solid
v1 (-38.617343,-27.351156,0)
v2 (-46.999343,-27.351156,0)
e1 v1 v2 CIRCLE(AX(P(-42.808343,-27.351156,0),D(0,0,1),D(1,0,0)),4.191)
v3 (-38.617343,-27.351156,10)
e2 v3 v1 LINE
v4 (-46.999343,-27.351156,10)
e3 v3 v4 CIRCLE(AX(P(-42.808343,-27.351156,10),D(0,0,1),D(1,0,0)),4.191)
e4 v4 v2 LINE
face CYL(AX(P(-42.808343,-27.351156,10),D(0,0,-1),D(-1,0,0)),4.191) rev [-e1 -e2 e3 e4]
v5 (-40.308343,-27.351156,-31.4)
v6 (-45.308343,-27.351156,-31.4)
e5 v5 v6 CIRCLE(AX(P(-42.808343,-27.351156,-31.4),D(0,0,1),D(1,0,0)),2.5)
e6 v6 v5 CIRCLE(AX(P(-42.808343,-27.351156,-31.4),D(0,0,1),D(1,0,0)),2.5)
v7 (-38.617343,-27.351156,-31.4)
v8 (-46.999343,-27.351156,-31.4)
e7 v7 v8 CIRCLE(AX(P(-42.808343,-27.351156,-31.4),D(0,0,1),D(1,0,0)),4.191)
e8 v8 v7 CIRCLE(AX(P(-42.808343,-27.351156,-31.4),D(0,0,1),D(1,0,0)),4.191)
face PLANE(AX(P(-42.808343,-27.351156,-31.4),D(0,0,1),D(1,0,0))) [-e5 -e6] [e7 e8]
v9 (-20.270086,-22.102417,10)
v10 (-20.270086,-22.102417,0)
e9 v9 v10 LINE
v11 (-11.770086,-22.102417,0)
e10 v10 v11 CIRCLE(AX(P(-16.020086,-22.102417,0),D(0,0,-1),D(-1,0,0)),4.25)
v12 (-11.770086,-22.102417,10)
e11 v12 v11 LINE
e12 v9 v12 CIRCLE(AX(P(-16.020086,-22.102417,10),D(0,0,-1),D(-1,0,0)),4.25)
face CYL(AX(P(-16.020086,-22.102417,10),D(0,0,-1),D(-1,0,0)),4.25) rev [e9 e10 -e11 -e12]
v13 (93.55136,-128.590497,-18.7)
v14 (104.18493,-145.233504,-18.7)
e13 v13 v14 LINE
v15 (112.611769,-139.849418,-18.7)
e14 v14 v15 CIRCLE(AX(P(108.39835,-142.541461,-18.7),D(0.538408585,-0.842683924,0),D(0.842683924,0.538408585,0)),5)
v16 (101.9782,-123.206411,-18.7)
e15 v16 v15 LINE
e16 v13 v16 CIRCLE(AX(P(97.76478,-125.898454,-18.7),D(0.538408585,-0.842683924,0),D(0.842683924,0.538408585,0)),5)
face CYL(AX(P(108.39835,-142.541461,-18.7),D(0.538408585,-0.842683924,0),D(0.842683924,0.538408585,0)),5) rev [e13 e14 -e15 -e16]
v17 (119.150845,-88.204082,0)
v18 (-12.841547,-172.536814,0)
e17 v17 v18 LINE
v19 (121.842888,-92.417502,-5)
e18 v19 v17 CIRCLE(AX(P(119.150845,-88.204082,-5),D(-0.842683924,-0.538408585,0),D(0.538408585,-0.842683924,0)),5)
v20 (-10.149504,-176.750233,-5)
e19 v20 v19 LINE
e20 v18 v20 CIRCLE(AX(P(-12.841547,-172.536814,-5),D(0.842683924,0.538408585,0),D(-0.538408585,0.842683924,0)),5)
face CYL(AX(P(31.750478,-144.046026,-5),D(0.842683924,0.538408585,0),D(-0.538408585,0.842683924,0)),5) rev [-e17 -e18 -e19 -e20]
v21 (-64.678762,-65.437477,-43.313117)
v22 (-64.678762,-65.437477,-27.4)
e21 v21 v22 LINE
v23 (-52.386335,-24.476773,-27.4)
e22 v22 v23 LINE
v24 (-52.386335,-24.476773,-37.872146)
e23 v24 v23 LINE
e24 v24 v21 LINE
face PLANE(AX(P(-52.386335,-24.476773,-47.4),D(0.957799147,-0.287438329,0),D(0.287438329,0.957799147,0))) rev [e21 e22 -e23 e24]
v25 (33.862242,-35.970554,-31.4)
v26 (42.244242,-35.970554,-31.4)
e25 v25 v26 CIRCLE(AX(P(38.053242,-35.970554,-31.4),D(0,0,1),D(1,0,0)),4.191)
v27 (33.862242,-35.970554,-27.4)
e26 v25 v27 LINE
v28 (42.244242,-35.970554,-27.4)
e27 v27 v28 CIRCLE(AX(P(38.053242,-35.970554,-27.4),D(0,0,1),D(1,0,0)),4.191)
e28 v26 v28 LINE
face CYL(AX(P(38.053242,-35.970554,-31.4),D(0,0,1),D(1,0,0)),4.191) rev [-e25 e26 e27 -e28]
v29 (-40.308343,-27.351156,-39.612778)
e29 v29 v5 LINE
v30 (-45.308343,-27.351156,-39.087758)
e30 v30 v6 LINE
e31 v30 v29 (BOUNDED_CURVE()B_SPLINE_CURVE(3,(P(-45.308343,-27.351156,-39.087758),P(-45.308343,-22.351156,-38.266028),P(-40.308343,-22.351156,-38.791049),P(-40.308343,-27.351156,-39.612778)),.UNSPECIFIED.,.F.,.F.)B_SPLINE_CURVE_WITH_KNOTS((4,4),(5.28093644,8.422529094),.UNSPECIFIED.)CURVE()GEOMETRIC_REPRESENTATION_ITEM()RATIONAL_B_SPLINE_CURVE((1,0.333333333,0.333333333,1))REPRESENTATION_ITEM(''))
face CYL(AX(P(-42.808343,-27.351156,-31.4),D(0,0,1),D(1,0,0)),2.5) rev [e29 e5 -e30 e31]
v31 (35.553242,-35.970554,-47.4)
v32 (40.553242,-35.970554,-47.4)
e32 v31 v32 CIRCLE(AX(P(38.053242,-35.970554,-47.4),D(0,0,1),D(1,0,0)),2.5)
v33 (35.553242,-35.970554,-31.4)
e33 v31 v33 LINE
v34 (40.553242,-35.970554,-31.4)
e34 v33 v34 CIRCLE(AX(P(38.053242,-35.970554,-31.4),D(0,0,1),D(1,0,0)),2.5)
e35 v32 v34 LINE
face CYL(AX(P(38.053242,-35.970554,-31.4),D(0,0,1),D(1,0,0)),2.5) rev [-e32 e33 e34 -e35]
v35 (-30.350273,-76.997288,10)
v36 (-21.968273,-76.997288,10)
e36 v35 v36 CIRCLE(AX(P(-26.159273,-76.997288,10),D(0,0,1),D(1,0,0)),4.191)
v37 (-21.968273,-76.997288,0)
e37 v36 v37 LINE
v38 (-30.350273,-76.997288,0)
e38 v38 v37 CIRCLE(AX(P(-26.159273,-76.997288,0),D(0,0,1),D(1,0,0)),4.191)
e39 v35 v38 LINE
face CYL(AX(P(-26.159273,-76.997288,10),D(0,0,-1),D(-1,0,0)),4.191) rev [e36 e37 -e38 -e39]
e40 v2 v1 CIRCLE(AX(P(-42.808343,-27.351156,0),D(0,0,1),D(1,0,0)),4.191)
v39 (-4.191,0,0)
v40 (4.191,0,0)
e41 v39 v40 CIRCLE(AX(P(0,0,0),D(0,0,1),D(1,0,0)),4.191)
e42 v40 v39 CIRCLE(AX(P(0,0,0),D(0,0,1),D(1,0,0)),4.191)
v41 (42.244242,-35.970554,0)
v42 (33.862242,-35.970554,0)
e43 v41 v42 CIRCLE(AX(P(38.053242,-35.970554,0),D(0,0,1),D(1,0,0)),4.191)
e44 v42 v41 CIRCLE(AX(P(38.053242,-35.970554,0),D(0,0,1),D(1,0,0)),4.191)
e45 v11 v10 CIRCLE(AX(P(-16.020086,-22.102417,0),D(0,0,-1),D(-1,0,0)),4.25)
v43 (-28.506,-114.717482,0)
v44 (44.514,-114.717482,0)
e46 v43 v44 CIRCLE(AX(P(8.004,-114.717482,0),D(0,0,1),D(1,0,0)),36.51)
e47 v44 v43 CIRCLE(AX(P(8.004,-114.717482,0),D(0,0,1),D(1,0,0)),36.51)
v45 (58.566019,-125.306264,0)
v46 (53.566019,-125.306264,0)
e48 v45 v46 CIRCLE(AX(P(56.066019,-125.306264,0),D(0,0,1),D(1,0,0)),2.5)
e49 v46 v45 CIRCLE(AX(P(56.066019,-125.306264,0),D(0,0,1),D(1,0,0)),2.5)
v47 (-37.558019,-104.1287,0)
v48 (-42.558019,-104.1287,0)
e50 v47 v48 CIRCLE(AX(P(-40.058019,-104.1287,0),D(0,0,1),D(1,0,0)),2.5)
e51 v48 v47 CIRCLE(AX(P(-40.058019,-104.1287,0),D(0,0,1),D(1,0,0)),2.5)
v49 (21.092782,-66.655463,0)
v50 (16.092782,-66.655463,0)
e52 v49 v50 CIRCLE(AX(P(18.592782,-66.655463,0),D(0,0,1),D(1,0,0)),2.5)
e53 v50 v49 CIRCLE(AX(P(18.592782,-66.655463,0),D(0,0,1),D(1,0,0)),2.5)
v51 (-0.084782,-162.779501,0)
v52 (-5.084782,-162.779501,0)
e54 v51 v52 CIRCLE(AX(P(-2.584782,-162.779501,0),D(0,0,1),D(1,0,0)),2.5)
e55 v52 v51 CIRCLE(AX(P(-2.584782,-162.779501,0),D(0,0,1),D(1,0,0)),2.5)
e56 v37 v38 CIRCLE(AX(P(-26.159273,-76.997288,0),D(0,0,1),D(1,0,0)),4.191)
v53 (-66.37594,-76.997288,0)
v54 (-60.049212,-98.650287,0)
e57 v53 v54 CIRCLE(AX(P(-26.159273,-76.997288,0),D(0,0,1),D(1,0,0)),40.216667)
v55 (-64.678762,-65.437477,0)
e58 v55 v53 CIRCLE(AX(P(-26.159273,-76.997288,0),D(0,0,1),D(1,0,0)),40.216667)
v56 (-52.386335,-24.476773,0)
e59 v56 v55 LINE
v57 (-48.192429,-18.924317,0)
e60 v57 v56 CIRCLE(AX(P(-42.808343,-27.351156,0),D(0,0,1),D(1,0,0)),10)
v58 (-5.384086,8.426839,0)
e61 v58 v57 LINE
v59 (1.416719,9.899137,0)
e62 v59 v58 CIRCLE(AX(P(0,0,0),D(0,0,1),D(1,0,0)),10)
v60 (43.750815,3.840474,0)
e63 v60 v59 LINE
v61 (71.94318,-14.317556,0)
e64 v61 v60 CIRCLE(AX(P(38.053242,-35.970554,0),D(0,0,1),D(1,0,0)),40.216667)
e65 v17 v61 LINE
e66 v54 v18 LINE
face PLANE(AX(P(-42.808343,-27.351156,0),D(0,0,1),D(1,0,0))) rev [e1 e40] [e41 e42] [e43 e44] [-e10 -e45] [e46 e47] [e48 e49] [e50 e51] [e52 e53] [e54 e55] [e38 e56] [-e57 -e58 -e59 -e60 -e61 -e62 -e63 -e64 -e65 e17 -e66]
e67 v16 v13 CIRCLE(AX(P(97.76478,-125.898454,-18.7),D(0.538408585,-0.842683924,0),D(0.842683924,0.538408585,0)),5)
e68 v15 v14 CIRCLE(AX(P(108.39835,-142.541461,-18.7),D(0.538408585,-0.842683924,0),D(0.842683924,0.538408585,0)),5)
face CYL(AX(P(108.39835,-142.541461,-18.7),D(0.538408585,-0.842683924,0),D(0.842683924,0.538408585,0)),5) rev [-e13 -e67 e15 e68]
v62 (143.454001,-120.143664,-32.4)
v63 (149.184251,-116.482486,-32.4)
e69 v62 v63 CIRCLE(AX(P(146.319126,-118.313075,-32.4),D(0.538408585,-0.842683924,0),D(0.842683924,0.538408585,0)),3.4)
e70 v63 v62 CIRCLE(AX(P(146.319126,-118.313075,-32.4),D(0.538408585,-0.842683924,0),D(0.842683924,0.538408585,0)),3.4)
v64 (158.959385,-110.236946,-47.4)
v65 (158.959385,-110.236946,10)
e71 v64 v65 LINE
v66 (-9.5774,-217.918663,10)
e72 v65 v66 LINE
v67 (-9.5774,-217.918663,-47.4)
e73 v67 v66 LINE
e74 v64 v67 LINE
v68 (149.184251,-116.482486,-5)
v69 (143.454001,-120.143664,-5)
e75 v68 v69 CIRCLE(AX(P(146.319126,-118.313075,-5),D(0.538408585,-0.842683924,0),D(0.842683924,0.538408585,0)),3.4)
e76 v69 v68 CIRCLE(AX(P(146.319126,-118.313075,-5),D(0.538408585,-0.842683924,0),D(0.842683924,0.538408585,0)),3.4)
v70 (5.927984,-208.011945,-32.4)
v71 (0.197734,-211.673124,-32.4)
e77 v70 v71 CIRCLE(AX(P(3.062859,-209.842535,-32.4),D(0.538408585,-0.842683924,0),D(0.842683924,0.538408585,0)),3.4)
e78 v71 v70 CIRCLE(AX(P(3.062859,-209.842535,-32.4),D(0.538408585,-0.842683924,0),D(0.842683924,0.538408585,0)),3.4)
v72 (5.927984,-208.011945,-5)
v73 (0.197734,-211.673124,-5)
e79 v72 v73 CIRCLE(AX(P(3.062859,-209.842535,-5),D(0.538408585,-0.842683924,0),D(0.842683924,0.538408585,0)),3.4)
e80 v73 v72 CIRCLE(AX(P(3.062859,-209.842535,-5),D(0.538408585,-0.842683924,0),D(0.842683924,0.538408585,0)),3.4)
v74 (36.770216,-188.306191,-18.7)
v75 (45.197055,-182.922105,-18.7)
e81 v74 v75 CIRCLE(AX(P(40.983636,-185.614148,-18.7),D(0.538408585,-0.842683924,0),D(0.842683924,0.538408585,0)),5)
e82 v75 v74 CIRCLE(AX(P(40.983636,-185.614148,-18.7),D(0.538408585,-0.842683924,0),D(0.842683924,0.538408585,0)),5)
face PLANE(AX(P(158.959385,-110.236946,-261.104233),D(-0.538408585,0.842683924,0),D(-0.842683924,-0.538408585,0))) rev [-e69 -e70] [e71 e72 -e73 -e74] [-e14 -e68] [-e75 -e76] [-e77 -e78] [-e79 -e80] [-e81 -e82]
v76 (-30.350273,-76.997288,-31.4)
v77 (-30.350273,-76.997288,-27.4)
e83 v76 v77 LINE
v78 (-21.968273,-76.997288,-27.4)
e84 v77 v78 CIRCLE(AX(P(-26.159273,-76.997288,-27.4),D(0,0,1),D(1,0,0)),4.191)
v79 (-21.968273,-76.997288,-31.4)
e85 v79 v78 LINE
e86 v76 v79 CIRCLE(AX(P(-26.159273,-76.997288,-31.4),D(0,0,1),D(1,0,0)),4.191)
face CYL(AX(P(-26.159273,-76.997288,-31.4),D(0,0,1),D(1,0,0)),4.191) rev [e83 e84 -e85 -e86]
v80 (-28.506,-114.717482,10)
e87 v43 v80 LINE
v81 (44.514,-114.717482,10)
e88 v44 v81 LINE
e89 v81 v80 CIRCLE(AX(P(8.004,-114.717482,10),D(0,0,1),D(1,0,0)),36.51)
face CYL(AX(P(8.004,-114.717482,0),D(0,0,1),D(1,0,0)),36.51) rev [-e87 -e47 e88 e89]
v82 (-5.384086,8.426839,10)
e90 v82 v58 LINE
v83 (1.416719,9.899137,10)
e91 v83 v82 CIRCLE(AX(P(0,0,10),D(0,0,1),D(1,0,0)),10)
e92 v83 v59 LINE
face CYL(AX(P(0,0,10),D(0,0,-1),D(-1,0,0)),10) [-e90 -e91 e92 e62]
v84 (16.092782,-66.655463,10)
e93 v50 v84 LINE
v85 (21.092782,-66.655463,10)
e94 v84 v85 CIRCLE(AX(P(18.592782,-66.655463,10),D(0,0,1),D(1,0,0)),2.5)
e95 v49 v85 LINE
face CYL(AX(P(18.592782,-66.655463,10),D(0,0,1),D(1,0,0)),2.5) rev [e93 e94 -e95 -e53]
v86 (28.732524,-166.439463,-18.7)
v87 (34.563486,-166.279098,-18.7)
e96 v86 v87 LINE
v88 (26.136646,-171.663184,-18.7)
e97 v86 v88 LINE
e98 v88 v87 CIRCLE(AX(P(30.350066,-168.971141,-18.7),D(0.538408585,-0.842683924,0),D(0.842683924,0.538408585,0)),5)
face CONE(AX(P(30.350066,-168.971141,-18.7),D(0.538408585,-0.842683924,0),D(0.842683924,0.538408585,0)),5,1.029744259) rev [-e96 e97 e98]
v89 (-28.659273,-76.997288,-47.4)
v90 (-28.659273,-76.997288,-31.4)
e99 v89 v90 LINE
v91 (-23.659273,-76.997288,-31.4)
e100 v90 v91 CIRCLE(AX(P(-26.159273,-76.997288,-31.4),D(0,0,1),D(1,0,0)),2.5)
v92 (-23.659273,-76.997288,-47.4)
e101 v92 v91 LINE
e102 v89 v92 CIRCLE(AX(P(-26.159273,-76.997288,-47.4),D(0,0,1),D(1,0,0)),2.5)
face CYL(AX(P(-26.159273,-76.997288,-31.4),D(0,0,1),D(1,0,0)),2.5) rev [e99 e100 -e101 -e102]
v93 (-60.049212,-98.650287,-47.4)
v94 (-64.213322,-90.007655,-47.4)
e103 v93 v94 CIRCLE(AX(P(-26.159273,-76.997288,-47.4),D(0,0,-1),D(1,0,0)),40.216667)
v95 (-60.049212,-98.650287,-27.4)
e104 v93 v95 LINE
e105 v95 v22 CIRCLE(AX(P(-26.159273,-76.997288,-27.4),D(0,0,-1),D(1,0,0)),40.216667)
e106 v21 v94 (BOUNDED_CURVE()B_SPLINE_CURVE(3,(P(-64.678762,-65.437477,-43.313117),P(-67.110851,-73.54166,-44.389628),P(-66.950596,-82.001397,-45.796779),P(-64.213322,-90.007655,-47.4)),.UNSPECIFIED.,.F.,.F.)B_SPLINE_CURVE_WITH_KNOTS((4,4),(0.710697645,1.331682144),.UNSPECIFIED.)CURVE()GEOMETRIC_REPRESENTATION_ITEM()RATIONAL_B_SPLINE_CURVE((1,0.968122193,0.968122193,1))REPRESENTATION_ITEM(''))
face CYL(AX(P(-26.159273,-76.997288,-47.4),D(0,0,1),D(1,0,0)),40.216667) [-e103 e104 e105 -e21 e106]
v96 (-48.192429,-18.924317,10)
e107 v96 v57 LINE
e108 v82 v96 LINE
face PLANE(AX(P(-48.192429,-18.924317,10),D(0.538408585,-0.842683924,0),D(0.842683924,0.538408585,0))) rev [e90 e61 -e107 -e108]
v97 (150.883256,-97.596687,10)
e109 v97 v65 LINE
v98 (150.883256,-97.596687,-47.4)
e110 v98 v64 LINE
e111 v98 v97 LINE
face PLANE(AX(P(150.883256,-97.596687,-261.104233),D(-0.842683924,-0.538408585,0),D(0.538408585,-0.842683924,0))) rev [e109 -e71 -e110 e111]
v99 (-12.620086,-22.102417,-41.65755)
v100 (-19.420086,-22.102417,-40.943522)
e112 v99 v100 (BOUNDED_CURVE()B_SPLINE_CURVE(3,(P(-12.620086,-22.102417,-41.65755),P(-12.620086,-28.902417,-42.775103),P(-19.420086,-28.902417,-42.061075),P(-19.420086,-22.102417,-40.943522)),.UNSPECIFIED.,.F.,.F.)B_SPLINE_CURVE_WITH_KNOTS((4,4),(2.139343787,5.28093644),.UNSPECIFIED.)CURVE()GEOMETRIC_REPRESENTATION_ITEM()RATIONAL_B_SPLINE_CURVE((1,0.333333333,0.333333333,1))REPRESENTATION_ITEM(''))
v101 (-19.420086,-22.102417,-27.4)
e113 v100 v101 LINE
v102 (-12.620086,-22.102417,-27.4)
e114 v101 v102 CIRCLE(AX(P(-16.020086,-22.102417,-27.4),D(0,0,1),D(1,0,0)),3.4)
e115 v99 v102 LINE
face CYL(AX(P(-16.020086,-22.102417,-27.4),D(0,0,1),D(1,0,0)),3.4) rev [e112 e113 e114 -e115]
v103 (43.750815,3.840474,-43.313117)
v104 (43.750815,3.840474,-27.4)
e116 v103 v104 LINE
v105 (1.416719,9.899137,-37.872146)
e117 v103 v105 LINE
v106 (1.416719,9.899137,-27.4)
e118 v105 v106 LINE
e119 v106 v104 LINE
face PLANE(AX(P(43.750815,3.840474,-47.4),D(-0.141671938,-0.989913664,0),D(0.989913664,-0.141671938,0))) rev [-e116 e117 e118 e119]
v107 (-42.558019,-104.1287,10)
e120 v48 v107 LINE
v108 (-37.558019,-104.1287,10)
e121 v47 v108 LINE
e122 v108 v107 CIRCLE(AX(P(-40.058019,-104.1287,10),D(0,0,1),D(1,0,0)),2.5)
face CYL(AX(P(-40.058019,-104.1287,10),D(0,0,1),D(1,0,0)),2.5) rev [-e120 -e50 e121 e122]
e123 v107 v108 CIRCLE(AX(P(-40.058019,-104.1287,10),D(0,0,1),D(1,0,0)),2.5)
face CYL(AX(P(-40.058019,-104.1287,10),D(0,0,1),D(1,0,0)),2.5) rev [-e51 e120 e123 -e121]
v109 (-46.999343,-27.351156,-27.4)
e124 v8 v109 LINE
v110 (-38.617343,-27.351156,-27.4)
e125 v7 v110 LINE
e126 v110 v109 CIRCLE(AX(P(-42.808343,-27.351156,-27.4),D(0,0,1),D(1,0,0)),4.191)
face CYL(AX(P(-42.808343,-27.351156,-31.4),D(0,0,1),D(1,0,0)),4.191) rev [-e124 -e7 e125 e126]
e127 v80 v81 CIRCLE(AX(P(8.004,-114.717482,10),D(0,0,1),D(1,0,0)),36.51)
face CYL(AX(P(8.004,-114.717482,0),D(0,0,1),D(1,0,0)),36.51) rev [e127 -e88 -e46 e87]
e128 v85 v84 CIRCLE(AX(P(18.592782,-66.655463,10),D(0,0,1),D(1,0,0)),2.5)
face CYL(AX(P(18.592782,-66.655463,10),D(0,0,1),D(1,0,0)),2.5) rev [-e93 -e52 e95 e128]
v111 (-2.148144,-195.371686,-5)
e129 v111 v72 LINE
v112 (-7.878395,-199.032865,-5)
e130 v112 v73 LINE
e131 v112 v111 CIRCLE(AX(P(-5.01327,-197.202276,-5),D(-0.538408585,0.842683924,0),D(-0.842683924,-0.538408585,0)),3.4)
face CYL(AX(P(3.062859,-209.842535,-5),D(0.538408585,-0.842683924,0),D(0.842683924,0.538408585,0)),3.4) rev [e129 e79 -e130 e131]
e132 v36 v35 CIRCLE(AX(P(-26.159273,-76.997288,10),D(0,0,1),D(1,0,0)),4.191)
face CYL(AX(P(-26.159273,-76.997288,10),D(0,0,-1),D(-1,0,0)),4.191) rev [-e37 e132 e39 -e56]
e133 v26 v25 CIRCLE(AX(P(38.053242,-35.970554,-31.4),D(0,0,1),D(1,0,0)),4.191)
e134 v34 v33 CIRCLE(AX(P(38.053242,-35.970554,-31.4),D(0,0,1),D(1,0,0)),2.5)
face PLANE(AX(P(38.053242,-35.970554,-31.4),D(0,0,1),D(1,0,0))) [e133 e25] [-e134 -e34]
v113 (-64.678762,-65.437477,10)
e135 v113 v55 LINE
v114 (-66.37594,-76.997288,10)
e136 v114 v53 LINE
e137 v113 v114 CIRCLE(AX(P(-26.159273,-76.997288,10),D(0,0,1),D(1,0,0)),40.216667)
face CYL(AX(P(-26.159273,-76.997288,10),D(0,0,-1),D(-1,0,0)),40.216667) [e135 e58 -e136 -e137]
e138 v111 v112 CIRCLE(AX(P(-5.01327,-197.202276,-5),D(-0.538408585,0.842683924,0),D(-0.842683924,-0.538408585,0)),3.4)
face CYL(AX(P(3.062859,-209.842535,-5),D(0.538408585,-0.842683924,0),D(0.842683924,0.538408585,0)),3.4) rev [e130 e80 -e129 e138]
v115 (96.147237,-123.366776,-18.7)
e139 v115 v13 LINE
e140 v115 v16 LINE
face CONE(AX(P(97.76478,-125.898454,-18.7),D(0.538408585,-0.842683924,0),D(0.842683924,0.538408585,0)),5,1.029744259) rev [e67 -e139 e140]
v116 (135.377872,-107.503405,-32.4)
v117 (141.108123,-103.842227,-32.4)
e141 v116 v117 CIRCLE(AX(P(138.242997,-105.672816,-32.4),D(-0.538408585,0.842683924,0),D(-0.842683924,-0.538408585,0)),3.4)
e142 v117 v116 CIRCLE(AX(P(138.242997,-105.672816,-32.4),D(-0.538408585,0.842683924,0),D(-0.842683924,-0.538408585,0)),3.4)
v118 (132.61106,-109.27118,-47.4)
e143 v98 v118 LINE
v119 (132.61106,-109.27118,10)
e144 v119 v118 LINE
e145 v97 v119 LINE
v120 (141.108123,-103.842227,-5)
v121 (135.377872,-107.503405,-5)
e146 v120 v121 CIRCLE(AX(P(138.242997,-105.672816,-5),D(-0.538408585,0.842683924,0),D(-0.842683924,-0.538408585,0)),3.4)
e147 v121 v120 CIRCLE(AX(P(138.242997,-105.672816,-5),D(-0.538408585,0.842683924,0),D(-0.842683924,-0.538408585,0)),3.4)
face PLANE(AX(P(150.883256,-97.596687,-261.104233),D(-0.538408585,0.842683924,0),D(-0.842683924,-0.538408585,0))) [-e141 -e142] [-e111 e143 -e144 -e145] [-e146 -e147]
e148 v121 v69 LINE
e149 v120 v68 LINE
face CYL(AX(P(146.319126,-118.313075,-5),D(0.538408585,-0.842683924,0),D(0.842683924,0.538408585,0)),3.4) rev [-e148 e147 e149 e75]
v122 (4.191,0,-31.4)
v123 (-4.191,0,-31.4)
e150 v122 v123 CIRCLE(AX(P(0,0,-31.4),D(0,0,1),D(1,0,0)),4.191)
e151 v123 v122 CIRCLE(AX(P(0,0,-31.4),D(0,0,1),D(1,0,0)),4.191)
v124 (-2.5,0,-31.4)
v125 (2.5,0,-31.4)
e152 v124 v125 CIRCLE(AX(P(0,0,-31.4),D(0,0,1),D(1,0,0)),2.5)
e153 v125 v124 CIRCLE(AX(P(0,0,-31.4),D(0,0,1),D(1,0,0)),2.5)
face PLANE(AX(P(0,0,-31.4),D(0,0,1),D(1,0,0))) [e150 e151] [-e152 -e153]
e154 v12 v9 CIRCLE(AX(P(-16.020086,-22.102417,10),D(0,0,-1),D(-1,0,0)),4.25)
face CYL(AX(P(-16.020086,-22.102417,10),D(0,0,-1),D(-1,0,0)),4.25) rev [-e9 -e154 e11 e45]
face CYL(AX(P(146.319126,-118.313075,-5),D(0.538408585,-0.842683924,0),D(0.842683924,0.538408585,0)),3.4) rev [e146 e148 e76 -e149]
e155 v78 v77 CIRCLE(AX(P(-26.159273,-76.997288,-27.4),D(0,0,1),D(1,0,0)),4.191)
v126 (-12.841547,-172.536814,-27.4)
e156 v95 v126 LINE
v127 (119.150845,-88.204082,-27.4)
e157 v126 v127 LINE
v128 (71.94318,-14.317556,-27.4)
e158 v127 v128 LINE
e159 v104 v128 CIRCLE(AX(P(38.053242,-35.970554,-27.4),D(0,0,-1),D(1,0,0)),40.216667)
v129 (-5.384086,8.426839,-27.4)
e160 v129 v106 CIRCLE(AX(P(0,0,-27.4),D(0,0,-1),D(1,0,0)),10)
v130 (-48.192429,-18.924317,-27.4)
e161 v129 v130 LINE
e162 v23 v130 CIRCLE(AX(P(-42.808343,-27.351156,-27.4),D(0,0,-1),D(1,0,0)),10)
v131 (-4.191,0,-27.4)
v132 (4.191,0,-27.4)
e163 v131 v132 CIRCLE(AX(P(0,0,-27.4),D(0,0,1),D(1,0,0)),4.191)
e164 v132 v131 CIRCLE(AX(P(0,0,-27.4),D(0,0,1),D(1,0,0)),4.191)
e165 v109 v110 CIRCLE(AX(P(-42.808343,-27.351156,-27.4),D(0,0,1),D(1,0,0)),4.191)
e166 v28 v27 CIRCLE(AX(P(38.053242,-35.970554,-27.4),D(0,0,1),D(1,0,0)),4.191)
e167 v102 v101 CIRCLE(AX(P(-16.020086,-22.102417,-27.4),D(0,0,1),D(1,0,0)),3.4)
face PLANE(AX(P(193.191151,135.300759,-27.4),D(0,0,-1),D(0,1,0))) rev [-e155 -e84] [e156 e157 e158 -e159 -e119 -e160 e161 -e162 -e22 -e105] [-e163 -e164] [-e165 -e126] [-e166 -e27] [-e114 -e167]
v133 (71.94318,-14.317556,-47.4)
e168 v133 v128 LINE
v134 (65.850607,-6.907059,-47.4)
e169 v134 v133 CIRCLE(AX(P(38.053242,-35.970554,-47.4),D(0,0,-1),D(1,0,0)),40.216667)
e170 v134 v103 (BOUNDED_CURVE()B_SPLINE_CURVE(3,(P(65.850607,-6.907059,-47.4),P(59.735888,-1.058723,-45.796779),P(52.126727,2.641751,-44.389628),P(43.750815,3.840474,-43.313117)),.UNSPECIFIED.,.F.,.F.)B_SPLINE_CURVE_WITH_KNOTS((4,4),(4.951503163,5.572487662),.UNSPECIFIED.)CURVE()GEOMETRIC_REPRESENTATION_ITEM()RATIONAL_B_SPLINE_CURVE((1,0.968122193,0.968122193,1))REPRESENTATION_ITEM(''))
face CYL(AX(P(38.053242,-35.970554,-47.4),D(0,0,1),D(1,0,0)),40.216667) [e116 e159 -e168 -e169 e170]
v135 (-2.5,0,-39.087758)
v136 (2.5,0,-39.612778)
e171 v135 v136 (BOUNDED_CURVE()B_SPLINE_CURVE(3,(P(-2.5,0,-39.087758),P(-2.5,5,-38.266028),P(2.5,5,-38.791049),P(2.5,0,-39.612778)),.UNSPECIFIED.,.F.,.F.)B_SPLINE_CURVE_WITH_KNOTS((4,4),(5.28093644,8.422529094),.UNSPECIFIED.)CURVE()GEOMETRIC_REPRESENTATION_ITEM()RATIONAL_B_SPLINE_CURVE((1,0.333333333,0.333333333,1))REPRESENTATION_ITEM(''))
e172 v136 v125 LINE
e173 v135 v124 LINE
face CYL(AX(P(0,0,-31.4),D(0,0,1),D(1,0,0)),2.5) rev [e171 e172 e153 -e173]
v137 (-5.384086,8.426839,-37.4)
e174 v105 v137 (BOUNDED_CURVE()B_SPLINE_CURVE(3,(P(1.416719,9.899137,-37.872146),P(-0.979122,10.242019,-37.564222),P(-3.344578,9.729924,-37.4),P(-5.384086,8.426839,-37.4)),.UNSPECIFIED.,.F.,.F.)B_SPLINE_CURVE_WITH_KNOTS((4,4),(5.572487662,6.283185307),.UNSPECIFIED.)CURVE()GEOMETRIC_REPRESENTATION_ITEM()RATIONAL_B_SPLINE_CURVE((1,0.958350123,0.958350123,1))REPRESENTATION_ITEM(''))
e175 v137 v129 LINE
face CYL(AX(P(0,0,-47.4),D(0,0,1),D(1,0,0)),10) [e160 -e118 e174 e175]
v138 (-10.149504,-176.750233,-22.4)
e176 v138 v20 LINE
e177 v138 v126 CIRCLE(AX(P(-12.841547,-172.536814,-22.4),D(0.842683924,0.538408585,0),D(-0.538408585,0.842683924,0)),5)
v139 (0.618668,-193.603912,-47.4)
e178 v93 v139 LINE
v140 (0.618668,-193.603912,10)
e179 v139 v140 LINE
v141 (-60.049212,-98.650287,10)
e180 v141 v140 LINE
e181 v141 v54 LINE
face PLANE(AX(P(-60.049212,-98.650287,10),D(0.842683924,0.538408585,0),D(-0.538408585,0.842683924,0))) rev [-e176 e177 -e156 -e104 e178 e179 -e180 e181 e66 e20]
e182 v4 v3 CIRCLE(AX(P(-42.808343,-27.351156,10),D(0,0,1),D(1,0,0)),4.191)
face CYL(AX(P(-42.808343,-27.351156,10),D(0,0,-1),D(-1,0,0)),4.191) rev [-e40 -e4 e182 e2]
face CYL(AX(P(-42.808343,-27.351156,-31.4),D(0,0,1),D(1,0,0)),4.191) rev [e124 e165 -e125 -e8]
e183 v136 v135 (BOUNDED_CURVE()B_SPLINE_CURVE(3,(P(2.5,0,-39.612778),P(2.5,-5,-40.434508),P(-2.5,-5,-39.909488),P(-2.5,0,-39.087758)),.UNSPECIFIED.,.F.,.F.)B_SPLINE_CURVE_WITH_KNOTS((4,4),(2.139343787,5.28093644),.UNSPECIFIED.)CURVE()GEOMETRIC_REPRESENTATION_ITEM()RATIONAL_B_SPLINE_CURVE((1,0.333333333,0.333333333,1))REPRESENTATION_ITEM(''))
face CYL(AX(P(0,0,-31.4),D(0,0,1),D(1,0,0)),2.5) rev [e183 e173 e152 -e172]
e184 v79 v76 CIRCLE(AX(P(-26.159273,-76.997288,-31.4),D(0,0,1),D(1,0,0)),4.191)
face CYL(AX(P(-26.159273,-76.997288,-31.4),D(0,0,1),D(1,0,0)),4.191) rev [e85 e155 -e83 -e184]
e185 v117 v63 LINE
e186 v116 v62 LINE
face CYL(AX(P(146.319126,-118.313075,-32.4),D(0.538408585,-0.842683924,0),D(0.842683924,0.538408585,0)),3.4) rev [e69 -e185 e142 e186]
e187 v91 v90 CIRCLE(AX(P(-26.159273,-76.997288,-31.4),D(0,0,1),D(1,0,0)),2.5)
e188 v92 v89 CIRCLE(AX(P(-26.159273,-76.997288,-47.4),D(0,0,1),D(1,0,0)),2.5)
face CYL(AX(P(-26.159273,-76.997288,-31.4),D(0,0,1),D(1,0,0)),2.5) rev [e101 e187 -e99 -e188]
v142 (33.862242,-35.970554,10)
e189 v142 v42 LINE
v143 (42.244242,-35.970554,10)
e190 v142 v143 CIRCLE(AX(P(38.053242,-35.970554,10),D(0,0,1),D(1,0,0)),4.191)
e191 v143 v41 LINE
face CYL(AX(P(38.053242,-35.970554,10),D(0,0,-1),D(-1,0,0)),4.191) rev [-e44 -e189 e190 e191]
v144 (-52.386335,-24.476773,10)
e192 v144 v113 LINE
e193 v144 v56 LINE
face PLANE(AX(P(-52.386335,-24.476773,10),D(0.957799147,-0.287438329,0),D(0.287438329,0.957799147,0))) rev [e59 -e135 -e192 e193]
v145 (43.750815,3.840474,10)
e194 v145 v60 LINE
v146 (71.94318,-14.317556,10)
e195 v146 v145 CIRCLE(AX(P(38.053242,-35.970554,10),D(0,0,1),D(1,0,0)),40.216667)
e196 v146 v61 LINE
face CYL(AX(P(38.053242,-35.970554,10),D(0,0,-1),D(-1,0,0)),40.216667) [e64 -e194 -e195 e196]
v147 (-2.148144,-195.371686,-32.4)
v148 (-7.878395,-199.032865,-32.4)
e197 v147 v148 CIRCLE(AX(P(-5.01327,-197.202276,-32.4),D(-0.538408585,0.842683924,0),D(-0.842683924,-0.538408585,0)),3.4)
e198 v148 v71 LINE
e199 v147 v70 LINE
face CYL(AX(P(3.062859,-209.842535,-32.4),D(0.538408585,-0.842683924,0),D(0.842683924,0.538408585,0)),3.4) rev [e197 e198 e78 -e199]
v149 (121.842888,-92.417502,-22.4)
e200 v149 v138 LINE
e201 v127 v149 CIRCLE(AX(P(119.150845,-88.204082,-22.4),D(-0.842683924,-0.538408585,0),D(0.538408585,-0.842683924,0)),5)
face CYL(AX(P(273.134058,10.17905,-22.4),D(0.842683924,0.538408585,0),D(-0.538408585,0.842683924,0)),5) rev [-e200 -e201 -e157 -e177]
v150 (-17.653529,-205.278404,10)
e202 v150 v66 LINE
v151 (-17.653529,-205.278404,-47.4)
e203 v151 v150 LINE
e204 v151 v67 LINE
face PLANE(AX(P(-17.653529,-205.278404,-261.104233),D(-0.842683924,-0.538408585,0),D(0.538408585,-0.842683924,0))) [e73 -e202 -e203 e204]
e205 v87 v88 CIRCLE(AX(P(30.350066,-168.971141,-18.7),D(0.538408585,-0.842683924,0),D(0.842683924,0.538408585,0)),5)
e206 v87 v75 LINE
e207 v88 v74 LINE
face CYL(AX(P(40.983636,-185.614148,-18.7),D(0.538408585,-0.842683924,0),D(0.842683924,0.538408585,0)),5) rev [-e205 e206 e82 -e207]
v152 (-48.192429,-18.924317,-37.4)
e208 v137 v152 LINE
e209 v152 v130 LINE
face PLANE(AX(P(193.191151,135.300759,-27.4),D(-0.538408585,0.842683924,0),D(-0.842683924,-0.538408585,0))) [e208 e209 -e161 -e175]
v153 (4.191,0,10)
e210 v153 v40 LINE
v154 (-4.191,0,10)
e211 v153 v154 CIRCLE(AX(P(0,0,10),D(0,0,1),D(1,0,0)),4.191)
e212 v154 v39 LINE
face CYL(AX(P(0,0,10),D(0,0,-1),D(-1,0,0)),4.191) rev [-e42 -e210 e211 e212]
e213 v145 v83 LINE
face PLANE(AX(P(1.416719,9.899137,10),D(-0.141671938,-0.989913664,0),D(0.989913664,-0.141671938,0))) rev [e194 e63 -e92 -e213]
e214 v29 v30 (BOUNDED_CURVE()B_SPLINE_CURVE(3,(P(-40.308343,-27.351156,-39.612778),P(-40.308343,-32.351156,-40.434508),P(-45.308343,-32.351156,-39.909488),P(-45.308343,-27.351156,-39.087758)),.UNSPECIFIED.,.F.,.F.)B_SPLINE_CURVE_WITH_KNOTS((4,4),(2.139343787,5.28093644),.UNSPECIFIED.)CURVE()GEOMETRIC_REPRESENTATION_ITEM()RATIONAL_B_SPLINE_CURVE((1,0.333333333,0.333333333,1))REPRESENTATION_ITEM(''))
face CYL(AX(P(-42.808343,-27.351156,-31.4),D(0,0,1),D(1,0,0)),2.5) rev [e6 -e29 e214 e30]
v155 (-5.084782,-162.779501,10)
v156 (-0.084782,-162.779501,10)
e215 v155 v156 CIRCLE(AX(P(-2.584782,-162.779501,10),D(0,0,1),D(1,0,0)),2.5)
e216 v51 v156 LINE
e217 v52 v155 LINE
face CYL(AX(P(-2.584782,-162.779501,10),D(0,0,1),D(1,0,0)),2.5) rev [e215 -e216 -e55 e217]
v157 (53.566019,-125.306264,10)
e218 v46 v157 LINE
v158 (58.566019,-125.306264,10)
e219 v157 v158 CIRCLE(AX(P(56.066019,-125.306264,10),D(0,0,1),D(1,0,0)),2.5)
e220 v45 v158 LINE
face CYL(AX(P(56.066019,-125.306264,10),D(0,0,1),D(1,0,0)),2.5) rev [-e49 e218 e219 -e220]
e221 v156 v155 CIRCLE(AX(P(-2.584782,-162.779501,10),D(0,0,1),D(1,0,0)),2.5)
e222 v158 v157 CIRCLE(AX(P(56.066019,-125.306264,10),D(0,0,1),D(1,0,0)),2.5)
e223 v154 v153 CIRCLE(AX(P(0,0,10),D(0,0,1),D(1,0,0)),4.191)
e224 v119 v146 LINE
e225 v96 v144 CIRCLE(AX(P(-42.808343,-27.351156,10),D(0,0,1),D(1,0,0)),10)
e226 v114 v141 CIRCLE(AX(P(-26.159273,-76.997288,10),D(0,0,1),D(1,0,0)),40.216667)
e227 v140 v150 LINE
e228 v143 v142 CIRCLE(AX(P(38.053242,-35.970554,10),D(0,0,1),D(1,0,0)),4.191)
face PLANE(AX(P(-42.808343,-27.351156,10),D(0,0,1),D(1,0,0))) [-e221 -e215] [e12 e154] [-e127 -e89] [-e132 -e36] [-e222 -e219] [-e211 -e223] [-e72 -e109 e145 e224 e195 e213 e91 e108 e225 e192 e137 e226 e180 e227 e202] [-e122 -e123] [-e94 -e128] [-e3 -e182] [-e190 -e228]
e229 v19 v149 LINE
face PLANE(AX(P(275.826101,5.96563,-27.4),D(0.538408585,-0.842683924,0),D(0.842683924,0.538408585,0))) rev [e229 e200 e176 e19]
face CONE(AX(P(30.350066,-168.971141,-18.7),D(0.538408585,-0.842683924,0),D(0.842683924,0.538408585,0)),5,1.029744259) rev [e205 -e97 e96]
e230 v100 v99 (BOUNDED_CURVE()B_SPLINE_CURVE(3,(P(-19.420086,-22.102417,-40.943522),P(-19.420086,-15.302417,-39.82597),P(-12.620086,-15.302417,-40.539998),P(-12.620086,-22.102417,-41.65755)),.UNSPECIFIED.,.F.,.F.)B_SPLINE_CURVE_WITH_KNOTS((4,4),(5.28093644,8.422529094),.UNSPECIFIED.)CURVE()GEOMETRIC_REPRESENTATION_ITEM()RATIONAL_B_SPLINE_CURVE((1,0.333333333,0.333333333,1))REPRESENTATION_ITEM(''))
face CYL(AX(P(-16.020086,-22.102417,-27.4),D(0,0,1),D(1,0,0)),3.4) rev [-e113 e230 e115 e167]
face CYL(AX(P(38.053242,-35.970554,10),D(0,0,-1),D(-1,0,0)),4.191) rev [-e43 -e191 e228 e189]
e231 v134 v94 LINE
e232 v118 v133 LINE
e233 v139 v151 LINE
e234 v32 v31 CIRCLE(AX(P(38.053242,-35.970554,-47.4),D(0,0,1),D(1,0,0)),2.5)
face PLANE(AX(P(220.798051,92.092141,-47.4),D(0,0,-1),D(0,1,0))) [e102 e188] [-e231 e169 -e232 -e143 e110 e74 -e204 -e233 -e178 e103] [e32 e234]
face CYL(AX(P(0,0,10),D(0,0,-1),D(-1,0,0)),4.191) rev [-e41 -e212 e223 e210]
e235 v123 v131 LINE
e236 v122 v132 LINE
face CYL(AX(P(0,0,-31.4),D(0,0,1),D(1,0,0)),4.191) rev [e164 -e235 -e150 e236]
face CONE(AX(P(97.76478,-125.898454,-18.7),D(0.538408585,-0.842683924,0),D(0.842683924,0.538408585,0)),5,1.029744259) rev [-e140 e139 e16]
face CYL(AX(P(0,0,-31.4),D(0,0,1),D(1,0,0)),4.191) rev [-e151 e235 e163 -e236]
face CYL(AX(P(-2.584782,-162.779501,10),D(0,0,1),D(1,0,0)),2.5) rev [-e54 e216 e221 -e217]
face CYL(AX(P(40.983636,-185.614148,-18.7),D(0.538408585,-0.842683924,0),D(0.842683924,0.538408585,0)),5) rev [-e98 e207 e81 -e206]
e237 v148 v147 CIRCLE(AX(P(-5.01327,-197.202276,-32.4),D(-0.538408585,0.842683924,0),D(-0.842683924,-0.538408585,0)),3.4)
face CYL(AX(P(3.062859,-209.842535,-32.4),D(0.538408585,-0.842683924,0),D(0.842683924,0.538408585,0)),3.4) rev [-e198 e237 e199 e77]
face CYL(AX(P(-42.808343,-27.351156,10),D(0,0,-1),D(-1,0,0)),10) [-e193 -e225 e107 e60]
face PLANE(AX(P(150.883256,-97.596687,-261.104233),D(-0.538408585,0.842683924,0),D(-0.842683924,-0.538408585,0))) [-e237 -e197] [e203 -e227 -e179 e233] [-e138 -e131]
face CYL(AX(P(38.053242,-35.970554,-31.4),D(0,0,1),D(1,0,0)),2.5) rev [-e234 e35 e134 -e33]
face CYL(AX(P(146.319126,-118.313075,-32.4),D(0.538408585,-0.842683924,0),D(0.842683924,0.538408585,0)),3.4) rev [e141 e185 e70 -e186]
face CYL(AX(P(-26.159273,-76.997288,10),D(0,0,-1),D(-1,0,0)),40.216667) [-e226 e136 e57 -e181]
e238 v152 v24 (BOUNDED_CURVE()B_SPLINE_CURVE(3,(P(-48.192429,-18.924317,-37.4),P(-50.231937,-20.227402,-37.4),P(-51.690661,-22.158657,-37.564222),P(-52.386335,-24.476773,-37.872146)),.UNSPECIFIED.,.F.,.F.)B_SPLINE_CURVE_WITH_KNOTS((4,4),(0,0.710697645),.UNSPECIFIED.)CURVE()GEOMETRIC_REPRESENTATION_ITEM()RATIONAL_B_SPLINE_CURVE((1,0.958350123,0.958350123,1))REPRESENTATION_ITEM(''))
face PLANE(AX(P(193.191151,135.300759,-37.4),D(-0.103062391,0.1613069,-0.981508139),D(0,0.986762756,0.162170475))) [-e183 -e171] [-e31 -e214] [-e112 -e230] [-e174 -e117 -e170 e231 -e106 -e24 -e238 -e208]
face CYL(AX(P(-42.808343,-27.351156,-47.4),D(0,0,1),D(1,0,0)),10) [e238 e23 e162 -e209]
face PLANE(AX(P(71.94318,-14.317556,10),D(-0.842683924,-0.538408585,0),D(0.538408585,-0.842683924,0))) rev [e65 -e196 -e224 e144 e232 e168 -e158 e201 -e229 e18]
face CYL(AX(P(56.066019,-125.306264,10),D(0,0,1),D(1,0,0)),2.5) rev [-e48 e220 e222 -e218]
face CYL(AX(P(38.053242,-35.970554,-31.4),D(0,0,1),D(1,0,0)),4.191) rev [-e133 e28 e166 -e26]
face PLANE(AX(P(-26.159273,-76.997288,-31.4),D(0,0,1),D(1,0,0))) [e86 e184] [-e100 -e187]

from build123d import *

# Parameters (mm, degrees)
SKETCH_1_R             = 4.191
EXTRUDE_1_DEPTH        = 10
SKETCH_2_R             = 2.5
CUT_EXTRUDE_1_DEPTH    = 10
SKETCH_3_W             = 156.633333356
SKETCH_3_H             = 10
EXTRUDE_2_DEPTH        = 22.68
SKETCH_4_R             = 36.51
CUT_EXTRUDE_2_DEPTH    = 215.91006095
HOLE_WIZARD_M6_1_D     = 5
EXTRUDE_3_DEPTH        = 156.633333356
CUT_EXTRUDE_3_DEPTH    = 238.627708353
CUT_EXTRUDE_START      = -4
SKETCH_10_R            = 4.191
CUT_EXTRUDE_4_DEPTH    = 4
HOLE_WIZARD_M6_2_D     = 5
FILLET_2_R             = 5
EXTRUDE_4_DEPTH        = 57.4
SKETCH_14_R            = 4.25
CUT_EXTRUDE_5_DEPTH    = 274.867467739
HOLE_WIZARD_M8_1_D     = 6.8
HOLE_WIZARD_M8_2_D     = 6.8
HOLE_WIZARD_M8_2_DEPTH = 19.75
HOLE_WIZARD_M8_2_TIP   = 2.042926105
MM_1_D                 = 10
MM_1_DEPTH             = 19.75
MM_1_TIP               = 3.004303095


with BuildPart() as part:
    # 草图1 → 凸台-拉伸1 (new body)
    with BuildSketch(Plane.XY):
        with BuildLine():
            Line((-48.192429183, -18.924316881), (-5.38408585, 8.426839239))
            ThreePointArc((-5.38408585, 8.426839239), (-2.115871946, 9.773591249), (1.416719377, 9.899136639))
            Line((1.416719377, 9.899136639), (43.750815051, 3.840473561))
            ThreePointArc((43.750815051, 3.840473561), (59.829864165, -2.159919824), (71.943180436, -14.317555701))
            Line((71.943180436, -14.317555701), (109.631781388, -73.305430372))
            Line((109.631781388, -73.305430372), (-22.360610574, -157.638161754))
            Line((-22.360610574, -157.638161754), (-60.049211526, -98.650287083))
            ThreePointArc((-60.049211526, -98.650287083), (-65.990843282, -82.549431417), (-64.6787621, -65.437476996))
            Line((-64.6787621, -65.437476996), (-52.386334807, -24.476772825))
            ThreePointArc((-52.386334807, -24.476772825), (-50.787903547, -21.323999346), (-48.192429183, -18.924316881))
        make_face()
        with Locations((-26.159273046, -76.997288483)):
            Circle(SKETCH_1_R, mode=Mode.SUBTRACT)
        with Locations((38.053241953, -35.970554303)):
            Circle(SKETCH_1_R, mode=Mode.SUBTRACT)
        Circle(SKETCH_1_R, mode=Mode.SUBTRACT)
        with Locations((-42.808343333, -27.35115612)):
            Circle(SKETCH_1_R, mode=Mode.SUBTRACT)
    extrude(amount=EXTRUDE_1_DEPTH)

    # 草图2 → 切除-拉伸1 (cut)
    with BuildSketch(Plane(origin=(0, 0, 0), x_dir=(-1, 0, 0), z_dir=(0, 0, -1))):
        with Locations((-8.003999953, -114.717481812)):
            Circle(SKETCH_2_R)
    extrude(amount=-CUT_EXTRUDE_1_DEPTH, mode=Mode.SUBTRACT)

    # 草图3 → 凸台-拉伸2 (add)
    with BuildSketch(Plane(origin=(65.039757073, -101.796218004, 0), x_dir=(0.8426839238753957, 0.538408585037392, 0), z_dir=(0.538408585037392, -0.8426839238753957, 0))):
        with Locations((-25.399999999, 5)):
            Rectangle(SKETCH_3_W, SKETCH_3_H)
    extrude(amount=EXTRUDE_2_DEPTH)

    # 草图4 → 切除-拉伸2 (cut, through all)
    with BuildSketch(Plane.XY.offset(10)):
        with Locations((8.003999953, -114.717481812)):
            Circle(SKETCH_4_R)
    extrude(amount=-CUT_EXTRUDE_2_DEPTH, mode=Mode.SUBTRACT)

    # M6 螺纹孔1 (through all)
    with Locations(Plane.XY.offset(10)):
        with Locations((-2.584781838, -162.779501122), (-40.058019357, -104.128700021), (56.066019263, -125.306263604), (18.592781745, -66.655462502)):
            Hole(HOLE_WIZARD_M6_1_D / 2)

    # 草图7 → 凸台-拉伸3 (add)
    with BuildSketch(Plane(origin=(-87.400367646, -55.84194375, 0), x_dir=(0, 0, 1), z_dir=(-0.8426839238753956, -0.5384085850373922, 0))):
        Polygon((-27.4, -143.48), (10, -143.48), (10, -163.48), (-47.4, -163.48), (-47.4, -41.275), (-37.4, 10), (-27.4, 10), align=None)
    extrude(amount=-EXTRUDE_3_DEPTH)

    # 草图8 → 切除-拉伸3 (cut, through all)
    with BuildSketch(Plane.XY.offset(-27.4)):
        with BuildLine():
            Line((71.943180436, -14.317555701), (39.207938465, 36.91762687))
            Line((39.207938465, 36.91762687), (-7.989717867, 44.981113167))
            Line((-7.989717867, 44.981113167), (-89.961386524, -17.397404979))
            Line((-89.961386524, -17.397404979), (-92.784453497, -47.415104511))
            Line((-92.784453497, -47.415104511), (-60.049211526, -98.650287083))
            ThreePointArc((-60.049211526, -98.650287083), (-65.990843282, -82.549431417), (-64.6787621, -65.437476996))
            Line((-64.6787621, -65.437476996), (-52.386334807, -24.476772825))
            ThreePointArc((-52.386334807, -24.476772825), (-50.787903547, -21.323999346), (-48.192429183, -18.924316881))
            Line((-48.192429183, -18.924316881), (-5.38408585, 8.426839239))
            ThreePointArc((-5.38408585, 8.426839239), (-2.115871946, 9.773591249), (1.416719377, 9.899136639))
            Line((1.416719377, 9.899136639), (43.750815051, 3.840473561))
            ThreePointArc((43.750815051, 3.840473561), (59.829864165, -2.159919824), (71.943180436, -14.317555701))
        make_face()
    extrude(amount=-CUT_EXTRUDE_3_DEPTH, mode=Mode.SUBTRACT)

    # 草图10 → 切除-拉伸4 (cut)
    with BuildSketch(Plane.XY.offset(-27.4).offset(CUT_EXTRUDE_START)):
        with Locations((38.053241953, -35.970554303)):
            Circle(SKETCH_10_R)
        with Locations((-26.159273046, -76.997288483)):
            Circle(SKETCH_10_R)
        with Locations((-42.808343333, -27.35115612)):
            Circle(SKETCH_10_R)
        Circle(SKETCH_10_R)
    extrude(amount=CUT_EXTRUDE_4_DEPTH, mode=Mode.SUBTRACT)

    # M6 螺纹孔2 (through all)
    with Locations(Plane.XY.offset(-31.4)):
        with Locations((0, 0), (38.053241953, -35.970554303), (-26.159273046, -76.997288483), (-42.808343333, -27.35115612)):
            Hole(HOLE_WIZARD_M6_2_D / 2)

    # 圆角2
    fillet_2_edges = [part.edges().sort_by_distance(p)[0] for p in [
        (55.846692116, -134.583867457, 0),
        (55.846692116, -134.583867457, -27.4),
    ]]
    fillet(fillet_2_edges, radius=FILLET_2_R)

    # 草图13 → 凸台-拉伸4 (add)
    with BuildSketch(Plane.XY.offset(10)):
        Polygon((150.883256204, -97.596687431), (-17.653528571, -205.278404438), (-9.577399795, -217.918663296), (158.95938498, -110.236946289), align=None)
    extrude(amount=-EXTRUDE_4_DEPTH)

    # 草图14 → 切除-拉伸5 (cut, through all)
    with BuildSketch(Plane(origin=(0, 0, 0), x_dir=(-1, 0, 0), z_dir=(0, 0, -1))):
        with Locations((16.020085816, -22.102417299)):
            Circle(SKETCH_14_R)
    extrude(amount=-CUT_EXTRUDE_5_DEPTH, mode=Mode.SUBTRACT)

    # M8 螺纹孔1 (through all)
    with Locations(Plane.XY.offset(-27.4)):
        with Locations((-16.020085816, -22.102417299)):
            Hole(HOLE_WIZARD_M8_1_D / 2)

    # M8 螺纹孔2
    with Locations(Plane(origin=(96.095164257, -150.402226733, 0), x_dir=(-0.8426839238753955, -0.538408585037392, 0), z_dir=(0.5384085850373921, -0.8426839238753956, 0))):
        with Locations((110.399999999, 5), (110.399999999, 32.4), (-59.600000001, 32.4), (-59.600000001, 5)):
            Hole(HOLE_WIZARD_M8_2_D / 2, depth=HOLE_WIZARD_M8_2_DEPTH)
            with Locations((0, 0, -(HOLE_WIZARD_M8_2_DEPTH + HOLE_WIZARD_M8_2_TIP / 2))):  # 118° drill point
                Cone(0, HOLE_WIZARD_M8_2_D / 2, HOLE_WIZARD_M8_2_TIP, mode=Mode.SUBTRACT)

    # 大小mm 暗销孔1
    with Locations(Plane(origin=(96.095164257, -150.402226733, 0), x_dir=(-0.8426839238753955, -0.538408585037392, 0), z_dir=(0.5384085850373921, -0.8426839238753956, 0))):
        with Locations((65.399999999, 18.7), (-14.600000001, 18.7)):
            Hole(MM_1_D / 2, depth=MM_1_DEPTH)
            with Locations((0, 0, -(MM_1_DEPTH + MM_1_TIP / 2))):  # 118° drill point
                Cone(0, MM_1_D / 2, MM_1_TIP, mode=Mode.SUBTRACT)


solid = part.part
